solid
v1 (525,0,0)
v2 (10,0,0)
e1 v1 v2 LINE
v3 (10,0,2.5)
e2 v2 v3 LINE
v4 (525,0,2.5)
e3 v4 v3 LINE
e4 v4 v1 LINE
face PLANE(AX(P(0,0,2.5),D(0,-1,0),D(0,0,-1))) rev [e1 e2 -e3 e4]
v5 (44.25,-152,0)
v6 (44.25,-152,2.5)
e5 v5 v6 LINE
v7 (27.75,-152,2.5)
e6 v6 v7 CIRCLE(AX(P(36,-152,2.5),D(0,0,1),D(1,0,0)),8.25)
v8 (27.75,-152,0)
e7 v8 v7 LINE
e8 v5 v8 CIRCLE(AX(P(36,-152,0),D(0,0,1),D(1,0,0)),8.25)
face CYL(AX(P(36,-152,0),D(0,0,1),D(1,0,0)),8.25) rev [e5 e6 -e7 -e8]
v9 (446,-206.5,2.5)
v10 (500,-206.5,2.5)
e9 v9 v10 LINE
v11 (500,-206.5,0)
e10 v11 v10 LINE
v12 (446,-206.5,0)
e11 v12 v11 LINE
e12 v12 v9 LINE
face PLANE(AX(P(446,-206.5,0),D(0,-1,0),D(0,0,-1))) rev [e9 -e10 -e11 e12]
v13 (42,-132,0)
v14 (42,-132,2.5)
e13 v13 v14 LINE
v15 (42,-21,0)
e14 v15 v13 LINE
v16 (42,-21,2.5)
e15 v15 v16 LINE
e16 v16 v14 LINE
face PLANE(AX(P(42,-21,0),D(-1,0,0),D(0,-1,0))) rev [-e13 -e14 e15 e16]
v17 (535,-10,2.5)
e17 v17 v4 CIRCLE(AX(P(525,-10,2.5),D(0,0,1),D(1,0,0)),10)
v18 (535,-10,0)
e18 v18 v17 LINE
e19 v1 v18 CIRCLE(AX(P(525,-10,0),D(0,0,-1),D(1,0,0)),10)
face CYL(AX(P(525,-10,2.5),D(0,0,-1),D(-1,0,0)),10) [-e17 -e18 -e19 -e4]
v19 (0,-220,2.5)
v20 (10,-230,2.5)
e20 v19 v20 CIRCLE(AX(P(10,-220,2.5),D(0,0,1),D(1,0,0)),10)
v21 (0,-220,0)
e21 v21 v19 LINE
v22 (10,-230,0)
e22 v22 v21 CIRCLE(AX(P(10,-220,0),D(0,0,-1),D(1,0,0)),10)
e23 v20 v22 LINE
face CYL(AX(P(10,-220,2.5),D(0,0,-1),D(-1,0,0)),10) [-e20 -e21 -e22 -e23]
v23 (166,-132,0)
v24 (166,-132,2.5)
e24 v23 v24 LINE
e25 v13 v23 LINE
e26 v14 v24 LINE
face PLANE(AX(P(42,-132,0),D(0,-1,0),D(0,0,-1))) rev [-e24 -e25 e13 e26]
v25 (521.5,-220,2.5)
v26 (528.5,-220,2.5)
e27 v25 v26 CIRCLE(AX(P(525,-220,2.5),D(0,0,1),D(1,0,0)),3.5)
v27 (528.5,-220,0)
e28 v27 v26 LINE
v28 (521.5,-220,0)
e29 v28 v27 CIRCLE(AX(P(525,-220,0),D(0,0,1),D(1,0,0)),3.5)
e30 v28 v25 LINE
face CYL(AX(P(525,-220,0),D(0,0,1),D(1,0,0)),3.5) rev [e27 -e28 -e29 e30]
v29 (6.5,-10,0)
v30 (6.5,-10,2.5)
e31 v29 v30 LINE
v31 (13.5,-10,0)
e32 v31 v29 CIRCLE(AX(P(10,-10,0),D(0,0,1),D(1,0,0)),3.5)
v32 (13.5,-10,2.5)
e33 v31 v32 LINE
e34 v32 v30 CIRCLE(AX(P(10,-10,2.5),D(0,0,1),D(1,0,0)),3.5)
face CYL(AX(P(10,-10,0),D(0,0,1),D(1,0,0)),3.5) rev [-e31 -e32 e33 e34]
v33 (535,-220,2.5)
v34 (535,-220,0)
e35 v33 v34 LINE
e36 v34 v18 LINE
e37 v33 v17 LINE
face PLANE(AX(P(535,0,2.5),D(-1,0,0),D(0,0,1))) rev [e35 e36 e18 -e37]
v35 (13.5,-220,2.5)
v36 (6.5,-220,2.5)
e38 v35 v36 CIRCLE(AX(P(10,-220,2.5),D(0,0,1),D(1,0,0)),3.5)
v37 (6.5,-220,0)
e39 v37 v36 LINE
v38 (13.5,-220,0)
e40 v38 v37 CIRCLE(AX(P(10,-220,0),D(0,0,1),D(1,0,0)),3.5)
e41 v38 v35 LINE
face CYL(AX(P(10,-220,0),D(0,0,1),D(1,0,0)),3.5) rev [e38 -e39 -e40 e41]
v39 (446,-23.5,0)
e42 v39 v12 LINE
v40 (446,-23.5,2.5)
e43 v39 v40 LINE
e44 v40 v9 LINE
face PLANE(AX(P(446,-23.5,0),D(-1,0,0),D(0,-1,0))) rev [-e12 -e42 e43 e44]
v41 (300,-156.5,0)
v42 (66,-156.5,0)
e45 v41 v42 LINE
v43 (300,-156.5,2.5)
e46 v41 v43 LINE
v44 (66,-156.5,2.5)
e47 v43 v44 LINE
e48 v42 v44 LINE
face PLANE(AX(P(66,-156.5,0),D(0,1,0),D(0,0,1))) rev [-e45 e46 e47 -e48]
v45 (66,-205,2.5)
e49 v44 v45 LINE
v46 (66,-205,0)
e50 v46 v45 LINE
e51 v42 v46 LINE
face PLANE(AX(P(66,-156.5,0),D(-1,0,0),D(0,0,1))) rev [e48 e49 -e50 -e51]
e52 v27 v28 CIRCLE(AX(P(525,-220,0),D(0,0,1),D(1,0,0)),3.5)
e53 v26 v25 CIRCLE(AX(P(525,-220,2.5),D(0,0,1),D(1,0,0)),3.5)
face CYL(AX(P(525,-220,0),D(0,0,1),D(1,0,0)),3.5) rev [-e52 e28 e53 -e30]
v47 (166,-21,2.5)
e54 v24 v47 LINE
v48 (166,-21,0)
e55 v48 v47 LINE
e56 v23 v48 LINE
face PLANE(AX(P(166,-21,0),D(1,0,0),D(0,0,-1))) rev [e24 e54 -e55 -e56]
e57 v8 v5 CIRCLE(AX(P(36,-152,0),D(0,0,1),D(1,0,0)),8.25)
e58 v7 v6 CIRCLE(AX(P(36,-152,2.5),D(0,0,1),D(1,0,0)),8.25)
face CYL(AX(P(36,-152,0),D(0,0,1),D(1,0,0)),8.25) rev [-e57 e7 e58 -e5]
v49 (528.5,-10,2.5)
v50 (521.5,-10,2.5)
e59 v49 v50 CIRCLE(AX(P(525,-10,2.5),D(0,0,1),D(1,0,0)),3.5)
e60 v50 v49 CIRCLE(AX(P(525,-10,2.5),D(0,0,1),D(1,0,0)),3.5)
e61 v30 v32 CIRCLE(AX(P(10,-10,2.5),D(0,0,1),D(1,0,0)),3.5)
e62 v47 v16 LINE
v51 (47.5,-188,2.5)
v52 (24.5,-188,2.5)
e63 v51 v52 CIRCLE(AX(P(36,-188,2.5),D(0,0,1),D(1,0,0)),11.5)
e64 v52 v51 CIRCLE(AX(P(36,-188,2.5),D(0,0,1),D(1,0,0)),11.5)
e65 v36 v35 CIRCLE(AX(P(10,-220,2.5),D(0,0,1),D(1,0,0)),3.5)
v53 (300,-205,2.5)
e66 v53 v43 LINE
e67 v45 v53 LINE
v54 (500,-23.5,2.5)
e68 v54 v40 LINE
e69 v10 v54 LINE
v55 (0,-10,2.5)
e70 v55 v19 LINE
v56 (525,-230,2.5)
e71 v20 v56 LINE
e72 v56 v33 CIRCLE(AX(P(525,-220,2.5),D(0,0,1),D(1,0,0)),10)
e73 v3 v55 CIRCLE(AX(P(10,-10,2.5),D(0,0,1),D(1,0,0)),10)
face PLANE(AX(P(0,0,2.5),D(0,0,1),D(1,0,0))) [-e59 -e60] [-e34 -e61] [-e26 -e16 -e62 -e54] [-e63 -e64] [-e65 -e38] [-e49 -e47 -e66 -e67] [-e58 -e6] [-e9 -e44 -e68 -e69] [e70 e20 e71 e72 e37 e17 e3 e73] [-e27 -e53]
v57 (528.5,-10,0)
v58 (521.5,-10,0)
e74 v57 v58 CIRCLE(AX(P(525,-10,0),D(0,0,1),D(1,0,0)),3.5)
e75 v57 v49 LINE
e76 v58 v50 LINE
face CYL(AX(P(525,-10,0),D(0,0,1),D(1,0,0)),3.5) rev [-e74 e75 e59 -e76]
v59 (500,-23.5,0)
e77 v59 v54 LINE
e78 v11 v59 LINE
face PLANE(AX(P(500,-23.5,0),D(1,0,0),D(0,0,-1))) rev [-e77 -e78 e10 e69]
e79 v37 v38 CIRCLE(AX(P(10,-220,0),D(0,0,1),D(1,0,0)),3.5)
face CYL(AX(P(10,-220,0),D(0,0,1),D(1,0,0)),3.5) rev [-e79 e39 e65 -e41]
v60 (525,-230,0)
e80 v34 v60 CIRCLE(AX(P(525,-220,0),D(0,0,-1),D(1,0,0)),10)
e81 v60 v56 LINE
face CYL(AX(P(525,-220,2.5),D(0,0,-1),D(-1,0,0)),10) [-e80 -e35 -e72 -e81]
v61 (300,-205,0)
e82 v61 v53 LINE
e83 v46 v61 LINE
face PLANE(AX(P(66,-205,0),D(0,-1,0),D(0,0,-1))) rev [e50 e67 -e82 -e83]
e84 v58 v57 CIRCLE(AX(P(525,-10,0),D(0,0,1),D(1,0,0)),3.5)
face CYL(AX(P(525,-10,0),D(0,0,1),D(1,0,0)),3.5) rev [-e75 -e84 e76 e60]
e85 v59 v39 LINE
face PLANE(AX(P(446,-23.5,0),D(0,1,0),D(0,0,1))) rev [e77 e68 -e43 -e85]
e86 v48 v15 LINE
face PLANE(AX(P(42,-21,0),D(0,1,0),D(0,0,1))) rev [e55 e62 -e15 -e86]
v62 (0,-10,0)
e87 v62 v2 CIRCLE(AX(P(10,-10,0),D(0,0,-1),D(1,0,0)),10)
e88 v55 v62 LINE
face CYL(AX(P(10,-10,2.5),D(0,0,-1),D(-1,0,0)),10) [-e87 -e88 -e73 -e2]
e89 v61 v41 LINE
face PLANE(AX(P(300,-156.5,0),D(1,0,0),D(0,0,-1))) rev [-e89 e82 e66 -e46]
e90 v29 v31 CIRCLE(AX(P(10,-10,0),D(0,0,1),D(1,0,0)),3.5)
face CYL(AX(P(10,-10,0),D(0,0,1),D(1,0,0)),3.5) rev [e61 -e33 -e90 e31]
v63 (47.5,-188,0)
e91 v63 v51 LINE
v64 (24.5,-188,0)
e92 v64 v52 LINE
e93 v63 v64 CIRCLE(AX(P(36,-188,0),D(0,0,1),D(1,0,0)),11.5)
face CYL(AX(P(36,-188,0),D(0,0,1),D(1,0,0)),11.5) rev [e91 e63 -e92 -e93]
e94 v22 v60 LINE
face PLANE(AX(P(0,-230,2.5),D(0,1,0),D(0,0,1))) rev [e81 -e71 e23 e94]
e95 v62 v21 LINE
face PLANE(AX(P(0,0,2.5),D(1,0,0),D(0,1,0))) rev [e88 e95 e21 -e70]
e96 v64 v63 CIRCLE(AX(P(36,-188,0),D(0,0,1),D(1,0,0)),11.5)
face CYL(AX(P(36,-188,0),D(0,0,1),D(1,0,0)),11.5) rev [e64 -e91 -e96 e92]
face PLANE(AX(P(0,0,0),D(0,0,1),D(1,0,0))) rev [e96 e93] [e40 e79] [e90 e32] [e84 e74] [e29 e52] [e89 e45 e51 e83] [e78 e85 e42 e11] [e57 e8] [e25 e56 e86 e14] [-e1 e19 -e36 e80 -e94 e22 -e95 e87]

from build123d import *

# Parameters (mm, degrees)
SKETCH1_W            = 535
SKETCH1_H            = 230
BOSS_EXTRUDE1_DEPTH  = 2.5
FILLET1_R            = 10
SKETCH2_R            = 3.5
CUT_EXTRUDE1_DEPTH   = 2.5
LPATTERN1_COUNT      = 2
LPATTERN1_PITCH      = 515
LPATTERN1_COUNT_DIR2 = 2
LPATTERN1_PITCH_DIR2 = 210
SKETCH3_W            = 124
SKETCH3_H            = 111
CUT_EXTRUDE2_DEPTH   = 2.5
SKETCH4_W            = 234
SKETCH4_H            = 48.5
CUT_EXTRUDE3_DEPTH   = 2.5
SKETCH5_R            = 11.5
CUT_EXTRUDE4_DEPTH   = 2.5
SKETCH7_R            = 8.25
CUT_EXTRUDE5_DEPTH   = 2.5
SKETCH8_W            = 54
SKETCH8_H            = 183
CUT_EXTRUDE6_DEPTH   = 2.5


with BuildPart() as part:
    # Sketch1 → Boss-Extrude1 (new body)
    with BuildSketch(Plane.XY):
        with Locations((267.5, -115)):
            Rectangle(SKETCH1_W, SKETCH1_H)
    extrude(amount=BOSS_EXTRUDE1_DEPTH)

    # Fillet1
    fillet1_edges = [part.edges().sort_by_distance(p)[0] for p in [
        (0, 0, 1.25),
        (535, 0, 1.25),
        (535, -230, 1.25),
        (0, -230, 1.25),
    ]]
    fillet(fillet1_edges, radius=FILLET1_R)

    # Sketch2 → Cut-Extrude1 (cut)
    with BuildSketch(Plane.XY.offset(2.5)):
        with Locations((10, -10)):
            Circle(SKETCH2_R)
    cut_extrude1 = extrude(amount=-CUT_EXTRUDE1_DEPTH, mode=Mode.SUBTRACT)

    # LPattern1: Cut-Extrude1 2 × 2
    with Locations(*[(i * LPATTERN1_PITCH, -j * LPATTERN1_PITCH_DIR2, 0) for i in range(LPATTERN1_COUNT) for j in range(LPATTERN1_COUNT_DIR2) if (i, j) != (0, 0)]):
        add(cut_extrude1, mode=Mode.SUBTRACT)

    # Sketch3 → Cut-Extrude2 (cut)
    with BuildSketch(Plane.XY.offset(2.5)):
        with Locations((104, -76.5)):
            Rectangle(SKETCH3_W, SKETCH3_H)
    extrude(amount=-CUT_EXTRUDE2_DEPTH, mode=Mode.SUBTRACT)

    # Sketch4 → Cut-Extrude3 (cut)
    with BuildSketch(Plane.XY.offset(2.5)):
        with Locations((183, -180.75)):
            Rectangle(SKETCH4_W, SKETCH4_H)
    extrude(amount=-CUT_EXTRUDE3_DEPTH, mode=Mode.SUBTRACT)

    # Sketch5 → Cut-Extrude4 (cut)
    with BuildSketch(Plane.XY.offset(2.5)):
        with Locations((36, -188)):
            Circle(SKETCH5_R)
    extrude(amount=-CUT_EXTRUDE4_DEPTH, mode=Mode.SUBTRACT)

    # Sketch7 → Cut-Extrude5 (cut)
    with BuildSketch(Plane.XY.offset(2.5)):
        with Locations((36, -152)):
            Circle(SKETCH7_R)
    extrude(amount=-CUT_EXTRUDE5_DEPTH, mode=Mode.SUBTRACT)

    # Sketch8 → Cut-Extrude6 (cut)
    with BuildSketch(Plane.XY.offset(2.5)):
        with Locations((473, -115)):
            Rectangle(SKETCH8_W, SKETCH8_H)
    extrude(amount=-CUT_EXTRUDE6_DEPTH, mode=Mode.SUBTRACT)


solid = part.part
